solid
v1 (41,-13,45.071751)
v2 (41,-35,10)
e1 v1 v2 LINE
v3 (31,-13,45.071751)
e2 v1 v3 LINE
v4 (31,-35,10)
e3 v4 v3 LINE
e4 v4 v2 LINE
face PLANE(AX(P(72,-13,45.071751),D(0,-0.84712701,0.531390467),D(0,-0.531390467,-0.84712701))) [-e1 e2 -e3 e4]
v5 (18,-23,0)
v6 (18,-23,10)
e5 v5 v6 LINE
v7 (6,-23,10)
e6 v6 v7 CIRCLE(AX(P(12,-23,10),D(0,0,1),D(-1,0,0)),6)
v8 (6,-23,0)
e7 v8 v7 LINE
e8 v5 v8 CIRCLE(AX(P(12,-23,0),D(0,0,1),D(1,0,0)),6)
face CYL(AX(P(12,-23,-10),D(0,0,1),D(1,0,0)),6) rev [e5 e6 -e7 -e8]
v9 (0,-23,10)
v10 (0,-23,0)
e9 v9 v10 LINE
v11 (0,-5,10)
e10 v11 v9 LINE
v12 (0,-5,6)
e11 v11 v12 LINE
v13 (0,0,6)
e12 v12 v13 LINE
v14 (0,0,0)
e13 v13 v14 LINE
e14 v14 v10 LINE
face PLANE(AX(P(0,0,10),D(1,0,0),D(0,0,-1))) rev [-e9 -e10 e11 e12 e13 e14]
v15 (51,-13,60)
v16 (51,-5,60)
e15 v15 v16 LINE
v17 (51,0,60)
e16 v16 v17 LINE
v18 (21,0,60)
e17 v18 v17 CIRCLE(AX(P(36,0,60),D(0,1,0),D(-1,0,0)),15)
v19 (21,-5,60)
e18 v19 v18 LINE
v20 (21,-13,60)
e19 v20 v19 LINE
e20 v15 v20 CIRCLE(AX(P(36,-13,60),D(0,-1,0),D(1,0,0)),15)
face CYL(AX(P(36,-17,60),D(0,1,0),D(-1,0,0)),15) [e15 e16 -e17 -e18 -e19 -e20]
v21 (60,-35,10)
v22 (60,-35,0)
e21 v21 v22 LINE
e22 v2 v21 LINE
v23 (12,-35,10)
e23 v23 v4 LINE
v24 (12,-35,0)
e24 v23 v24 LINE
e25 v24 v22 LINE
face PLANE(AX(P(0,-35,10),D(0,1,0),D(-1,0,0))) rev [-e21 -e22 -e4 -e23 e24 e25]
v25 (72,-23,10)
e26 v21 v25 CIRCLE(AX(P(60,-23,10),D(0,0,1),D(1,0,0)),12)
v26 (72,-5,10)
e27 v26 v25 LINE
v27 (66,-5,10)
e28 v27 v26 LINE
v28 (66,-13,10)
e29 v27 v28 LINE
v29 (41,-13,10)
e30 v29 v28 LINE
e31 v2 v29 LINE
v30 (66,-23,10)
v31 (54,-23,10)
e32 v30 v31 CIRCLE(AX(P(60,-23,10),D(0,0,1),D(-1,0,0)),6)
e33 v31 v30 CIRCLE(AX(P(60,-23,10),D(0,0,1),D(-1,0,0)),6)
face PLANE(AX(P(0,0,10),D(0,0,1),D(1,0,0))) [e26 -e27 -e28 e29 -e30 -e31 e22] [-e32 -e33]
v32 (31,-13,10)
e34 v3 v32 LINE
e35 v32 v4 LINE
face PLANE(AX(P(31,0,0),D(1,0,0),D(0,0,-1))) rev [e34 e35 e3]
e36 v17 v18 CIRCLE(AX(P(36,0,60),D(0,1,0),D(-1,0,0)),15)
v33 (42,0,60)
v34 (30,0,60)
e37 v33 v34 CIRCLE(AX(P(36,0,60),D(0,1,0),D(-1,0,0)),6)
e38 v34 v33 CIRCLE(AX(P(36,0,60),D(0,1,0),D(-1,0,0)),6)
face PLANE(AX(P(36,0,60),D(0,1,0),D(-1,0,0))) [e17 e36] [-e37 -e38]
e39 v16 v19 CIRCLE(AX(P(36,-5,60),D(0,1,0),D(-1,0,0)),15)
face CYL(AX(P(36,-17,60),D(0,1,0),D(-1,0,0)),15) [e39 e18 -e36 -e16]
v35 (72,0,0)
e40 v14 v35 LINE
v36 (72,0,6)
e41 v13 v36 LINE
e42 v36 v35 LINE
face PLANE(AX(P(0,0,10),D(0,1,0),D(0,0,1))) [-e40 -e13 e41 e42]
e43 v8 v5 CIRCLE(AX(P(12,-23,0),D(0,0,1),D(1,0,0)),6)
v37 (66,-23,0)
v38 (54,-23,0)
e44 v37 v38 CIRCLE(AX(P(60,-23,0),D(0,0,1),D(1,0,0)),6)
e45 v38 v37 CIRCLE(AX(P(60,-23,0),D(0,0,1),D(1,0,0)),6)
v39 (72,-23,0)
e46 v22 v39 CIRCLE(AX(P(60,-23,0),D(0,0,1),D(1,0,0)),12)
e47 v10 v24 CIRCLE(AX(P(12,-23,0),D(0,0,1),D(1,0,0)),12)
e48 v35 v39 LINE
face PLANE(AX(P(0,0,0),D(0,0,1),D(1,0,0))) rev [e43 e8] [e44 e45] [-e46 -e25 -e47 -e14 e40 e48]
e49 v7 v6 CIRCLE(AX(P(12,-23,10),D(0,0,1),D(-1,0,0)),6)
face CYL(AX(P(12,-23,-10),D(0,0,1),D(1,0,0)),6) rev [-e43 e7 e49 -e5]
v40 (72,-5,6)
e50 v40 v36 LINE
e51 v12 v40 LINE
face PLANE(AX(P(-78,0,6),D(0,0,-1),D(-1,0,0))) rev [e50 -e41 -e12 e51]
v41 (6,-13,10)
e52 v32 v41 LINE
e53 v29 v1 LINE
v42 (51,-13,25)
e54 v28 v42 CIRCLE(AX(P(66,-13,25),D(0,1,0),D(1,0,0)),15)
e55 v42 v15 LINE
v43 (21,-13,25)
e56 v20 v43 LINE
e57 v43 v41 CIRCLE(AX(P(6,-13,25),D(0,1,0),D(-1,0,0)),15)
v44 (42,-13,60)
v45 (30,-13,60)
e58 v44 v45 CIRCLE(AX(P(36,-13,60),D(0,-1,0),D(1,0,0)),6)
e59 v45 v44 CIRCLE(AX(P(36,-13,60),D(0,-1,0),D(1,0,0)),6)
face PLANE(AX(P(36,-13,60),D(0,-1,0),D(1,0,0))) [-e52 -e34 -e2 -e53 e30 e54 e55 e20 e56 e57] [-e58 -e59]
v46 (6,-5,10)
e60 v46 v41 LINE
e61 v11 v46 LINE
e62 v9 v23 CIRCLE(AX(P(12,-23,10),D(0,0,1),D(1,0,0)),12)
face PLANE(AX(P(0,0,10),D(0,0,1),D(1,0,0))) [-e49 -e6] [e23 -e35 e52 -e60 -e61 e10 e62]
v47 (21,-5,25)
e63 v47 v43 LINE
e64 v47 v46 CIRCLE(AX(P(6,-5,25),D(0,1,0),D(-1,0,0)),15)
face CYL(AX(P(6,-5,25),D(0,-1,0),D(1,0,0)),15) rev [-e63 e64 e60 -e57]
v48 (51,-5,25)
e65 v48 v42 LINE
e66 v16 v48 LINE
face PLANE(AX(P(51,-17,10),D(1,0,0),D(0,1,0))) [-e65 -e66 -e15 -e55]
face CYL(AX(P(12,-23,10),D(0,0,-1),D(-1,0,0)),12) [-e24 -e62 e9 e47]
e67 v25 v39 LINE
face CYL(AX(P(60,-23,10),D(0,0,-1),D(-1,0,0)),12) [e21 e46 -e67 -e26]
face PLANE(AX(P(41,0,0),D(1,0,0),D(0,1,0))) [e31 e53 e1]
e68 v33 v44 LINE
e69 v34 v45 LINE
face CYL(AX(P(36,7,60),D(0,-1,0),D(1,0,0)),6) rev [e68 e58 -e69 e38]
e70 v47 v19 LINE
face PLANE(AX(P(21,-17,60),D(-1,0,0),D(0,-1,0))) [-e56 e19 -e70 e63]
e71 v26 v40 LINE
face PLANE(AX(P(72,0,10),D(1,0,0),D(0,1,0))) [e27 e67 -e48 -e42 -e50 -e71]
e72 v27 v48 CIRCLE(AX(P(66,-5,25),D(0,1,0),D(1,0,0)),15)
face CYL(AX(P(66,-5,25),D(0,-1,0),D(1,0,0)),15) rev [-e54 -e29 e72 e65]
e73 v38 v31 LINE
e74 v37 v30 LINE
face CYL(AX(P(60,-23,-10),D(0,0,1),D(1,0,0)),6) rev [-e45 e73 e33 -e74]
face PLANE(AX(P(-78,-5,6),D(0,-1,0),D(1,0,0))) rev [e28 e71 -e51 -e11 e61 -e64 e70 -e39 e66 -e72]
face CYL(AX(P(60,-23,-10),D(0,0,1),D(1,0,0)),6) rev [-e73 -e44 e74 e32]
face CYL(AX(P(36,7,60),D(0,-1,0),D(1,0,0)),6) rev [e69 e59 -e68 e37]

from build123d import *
from build123d.topology import SkipClean

# Parameters (mm, degrees)
BASE_PLATE_PROFILE_W   = 12
BASE_PLATE_PROFILE_H   = 23
BASE_PLATE_DEPTH       = 10
GROOVE_PROFILE_4X5_W   = 4
GROOVE_PROFILE_4X5_H   = 5
GROOVE_CUT_4X5_DEPTH   = 150
ARM_DEPTH              = 12
EYE_START              = 5
EYE_BOSS_SKETCH_30_R   = 15
EYE_BOSS_30_DEPTH      = 5
ARM_START              = -4
ARM_RELIEF_CUT_DEPTH   = 4
EYE_HOLE_SKETCH_12_R   = 6
EYE_HOLE_12_DEPTH      = 20
UPRIGHT_RIB_DEPTH      = 8
CROSS_HOLE_SKETCH_12_R = 6
CROSS_HOLE_12_DEPTH    = 20
UPRIGHT_WEB_DEPTH      = 72
WEB_TRIM_CUT_1_DEPTH   = 31
WEB_TRIM_CUT_2_DEPTH   = 31


with BuildPart() as part:
    # Base Plate Profile → Base Plate (new body)
    with BuildSketch(Plane.XY):
        Polygon((36, 0), (12, 0), (12, -23), (60, -23), (60, 0), align=None)
        with Locations((6, -11.5)):
            Rectangle(BASE_PLATE_PROFILE_W, BASE_PLATE_PROFILE_H)
        with Locations((66, -11.5)):
            Rectangle(BASE_PLATE_PROFILE_W, BASE_PLATE_PROFILE_H)
        with BuildLine():
            Line((12, -35), (60, -35))
            ThreePointArc((60, -35), (68.485281374, -31.485281374), (72, -23))
            Line((72, -23), (0, -23))
            ThreePointArc((0, -23), (3.514718626, -31.485281374), (12, -35))
        make_face()
    extrude(amount=BASE_PLATE_DEPTH)

    # Groove Profile 4x5 → Groove Cut 4x5 (cut)
    with BuildSketch(Plane(origin=(72, 0, 0), x_dir=(0, 0, -1), z_dir=(1, 0, 0))):
        with Locations((-8, -2.5)):
            Rectangle(GROOVE_PROFILE_4X5_W, GROOVE_PROFILE_4X5_H)
    extrude(amount=-GROOVE_CUT_4X5_DEPTH, mode=Mode.SUBTRACT)

    # Arm Profile → Arm (add)
    with BuildSketch(Plane(origin=(0, -5, 0), x_dir=(1, 0, 0), z_dir=(0, 1, 0))):
        with BuildLine():
            Line((21, -60), (21, -10))
            Line((21, -10), (51, -10))
            Line((51, -10), (51, -60))
            ThreePointArc((51, -60), (36, -75), (21, -60))
        make_face()
    extrude(amount=-ARM_DEPTH)

    # Eye Boss Sketch Ø30 → Eye Boss Ø30 (add)
    with SkipClean():  # the faces are left unmerged after this step: merging them gives an invalid solid
        with BuildSketch(Plane(origin=(0, -5, 0), x_dir=(1, 0, 0), z_dir=(0, 1, 0)).offset(EYE_START)):
            with Locations(Location((36, -60, 0), (0, 0, 180))):
                Circle(EYE_BOSS_SKETCH_30_R)
        extrude(amount=-EYE_BOSS_30_DEPTH)

    # Arm Relief Profile → Arm Relief Cut (cut)
    with SkipClean():  # the faces are left unmerged after this step: merging them gives an invalid solid
        with BuildSketch(Plane.XZ.offset(17).offset(ARM_START)):
            with BuildLine():
                Line((21, 10), (21, 60))
                ThreePointArc((21, 60), (36, 75), (51, 60))
                Line((51, 60), (51, 10))
                Line((51, 10), (21, 10))
            make_face()
        extrude(amount=ARM_RELIEF_CUT_DEPTH, mode=Mode.SUBTRACT)

    # Eye Hole Sketch Ø12 → Eye Hole Ø12 (cut)
    with SkipClean():  # the faces are left unmerged after this step: merging them gives an invalid solid
        with BuildSketch(Plane.XZ.offset(13)):
            with Locations((36, 60)):
                Circle(EYE_HOLE_SKETCH_12_R)
        extrude(amount=-EYE_HOLE_12_DEPTH, mode=Mode.SUBTRACT)

    # Upright Rib Profile → Upright Rib (add)
    with SkipClean():  # the faces are left unmerged after this step: merging them gives an invalid solid
        with BuildSketch(Plane.XZ.offset(13)):
            with BuildLine():
                Line((6, 10), (21, 10))
                Line((21, 10), (21, 25))
                ThreePointArc((21, 25), (16.606601718, 14.393398282), (6, 10))
            make_face()
            with BuildLine():
                Line((51, 25), (51, 10))
                Line((51, 10), (66, 10))
                ThreePointArc((66, 10), (55.393398282, 14.393398282), (51, 25))
            make_face()
        extrude(amount=-UPRIGHT_RIB_DEPTH)

    # Cross Hole Sketch Ø12 → Cross Hole Ø12 (cut)
    with SkipClean():  # the faces are left unmerged after this step: merging them gives an invalid solid
        with BuildSketch(Plane.XY.offset(10)):
            with Locations((12, -23)):
                Circle(CROSS_HOLE_SKETCH_12_R)
            with Locations((60, -23)):
                Circle(CROSS_HOLE_SKETCH_12_R)
        extrude(amount=-CROSS_HOLE_12_DEPTH, mode=Mode.SUBTRACT)

    # Upright Web Profile → Upright Web (add)
    with SkipClean():  # the faces are left unmerged after this step: merging them gives an invalid solid
        with BuildSketch(Plane.ZY):
            Polygon((10, -13), (45.07175112, -13), (10, -35), align=None)
        extrude(amount=-UPRIGHT_WEB_DEPTH)

    # Web Trim Profile 1 → Web Trim Cut 1 (cut)
    with SkipClean():  # the faces are left unmerged after this step: merging them gives an invalid solid
        with BuildSketch(Plane(origin=(72, 0, 0), x_dir=(0, 0, -1), z_dir=(1, 0, 0))):
            Polygon((-45.07175112, -13), (-10, -13), (-10, -35), align=None)
        extrude(amount=-WEB_TRIM_CUT_1_DEPTH, mode=Mode.SUBTRACT)

    # Web Trim Profile 2 → Web Trim Cut 2 (cut)
    with SkipClean():  # the faces are left unmerged after this step: merging them gives an invalid solid
        with BuildSketch(Plane.ZY):
            Polygon((10, -35), (10, -13), (45.07175112, -13), align=None)
        extrude(amount=-WEB_TRIM_CUT_2_DEPTH, mode=Mode.SUBTRACT)


solid = part.part
